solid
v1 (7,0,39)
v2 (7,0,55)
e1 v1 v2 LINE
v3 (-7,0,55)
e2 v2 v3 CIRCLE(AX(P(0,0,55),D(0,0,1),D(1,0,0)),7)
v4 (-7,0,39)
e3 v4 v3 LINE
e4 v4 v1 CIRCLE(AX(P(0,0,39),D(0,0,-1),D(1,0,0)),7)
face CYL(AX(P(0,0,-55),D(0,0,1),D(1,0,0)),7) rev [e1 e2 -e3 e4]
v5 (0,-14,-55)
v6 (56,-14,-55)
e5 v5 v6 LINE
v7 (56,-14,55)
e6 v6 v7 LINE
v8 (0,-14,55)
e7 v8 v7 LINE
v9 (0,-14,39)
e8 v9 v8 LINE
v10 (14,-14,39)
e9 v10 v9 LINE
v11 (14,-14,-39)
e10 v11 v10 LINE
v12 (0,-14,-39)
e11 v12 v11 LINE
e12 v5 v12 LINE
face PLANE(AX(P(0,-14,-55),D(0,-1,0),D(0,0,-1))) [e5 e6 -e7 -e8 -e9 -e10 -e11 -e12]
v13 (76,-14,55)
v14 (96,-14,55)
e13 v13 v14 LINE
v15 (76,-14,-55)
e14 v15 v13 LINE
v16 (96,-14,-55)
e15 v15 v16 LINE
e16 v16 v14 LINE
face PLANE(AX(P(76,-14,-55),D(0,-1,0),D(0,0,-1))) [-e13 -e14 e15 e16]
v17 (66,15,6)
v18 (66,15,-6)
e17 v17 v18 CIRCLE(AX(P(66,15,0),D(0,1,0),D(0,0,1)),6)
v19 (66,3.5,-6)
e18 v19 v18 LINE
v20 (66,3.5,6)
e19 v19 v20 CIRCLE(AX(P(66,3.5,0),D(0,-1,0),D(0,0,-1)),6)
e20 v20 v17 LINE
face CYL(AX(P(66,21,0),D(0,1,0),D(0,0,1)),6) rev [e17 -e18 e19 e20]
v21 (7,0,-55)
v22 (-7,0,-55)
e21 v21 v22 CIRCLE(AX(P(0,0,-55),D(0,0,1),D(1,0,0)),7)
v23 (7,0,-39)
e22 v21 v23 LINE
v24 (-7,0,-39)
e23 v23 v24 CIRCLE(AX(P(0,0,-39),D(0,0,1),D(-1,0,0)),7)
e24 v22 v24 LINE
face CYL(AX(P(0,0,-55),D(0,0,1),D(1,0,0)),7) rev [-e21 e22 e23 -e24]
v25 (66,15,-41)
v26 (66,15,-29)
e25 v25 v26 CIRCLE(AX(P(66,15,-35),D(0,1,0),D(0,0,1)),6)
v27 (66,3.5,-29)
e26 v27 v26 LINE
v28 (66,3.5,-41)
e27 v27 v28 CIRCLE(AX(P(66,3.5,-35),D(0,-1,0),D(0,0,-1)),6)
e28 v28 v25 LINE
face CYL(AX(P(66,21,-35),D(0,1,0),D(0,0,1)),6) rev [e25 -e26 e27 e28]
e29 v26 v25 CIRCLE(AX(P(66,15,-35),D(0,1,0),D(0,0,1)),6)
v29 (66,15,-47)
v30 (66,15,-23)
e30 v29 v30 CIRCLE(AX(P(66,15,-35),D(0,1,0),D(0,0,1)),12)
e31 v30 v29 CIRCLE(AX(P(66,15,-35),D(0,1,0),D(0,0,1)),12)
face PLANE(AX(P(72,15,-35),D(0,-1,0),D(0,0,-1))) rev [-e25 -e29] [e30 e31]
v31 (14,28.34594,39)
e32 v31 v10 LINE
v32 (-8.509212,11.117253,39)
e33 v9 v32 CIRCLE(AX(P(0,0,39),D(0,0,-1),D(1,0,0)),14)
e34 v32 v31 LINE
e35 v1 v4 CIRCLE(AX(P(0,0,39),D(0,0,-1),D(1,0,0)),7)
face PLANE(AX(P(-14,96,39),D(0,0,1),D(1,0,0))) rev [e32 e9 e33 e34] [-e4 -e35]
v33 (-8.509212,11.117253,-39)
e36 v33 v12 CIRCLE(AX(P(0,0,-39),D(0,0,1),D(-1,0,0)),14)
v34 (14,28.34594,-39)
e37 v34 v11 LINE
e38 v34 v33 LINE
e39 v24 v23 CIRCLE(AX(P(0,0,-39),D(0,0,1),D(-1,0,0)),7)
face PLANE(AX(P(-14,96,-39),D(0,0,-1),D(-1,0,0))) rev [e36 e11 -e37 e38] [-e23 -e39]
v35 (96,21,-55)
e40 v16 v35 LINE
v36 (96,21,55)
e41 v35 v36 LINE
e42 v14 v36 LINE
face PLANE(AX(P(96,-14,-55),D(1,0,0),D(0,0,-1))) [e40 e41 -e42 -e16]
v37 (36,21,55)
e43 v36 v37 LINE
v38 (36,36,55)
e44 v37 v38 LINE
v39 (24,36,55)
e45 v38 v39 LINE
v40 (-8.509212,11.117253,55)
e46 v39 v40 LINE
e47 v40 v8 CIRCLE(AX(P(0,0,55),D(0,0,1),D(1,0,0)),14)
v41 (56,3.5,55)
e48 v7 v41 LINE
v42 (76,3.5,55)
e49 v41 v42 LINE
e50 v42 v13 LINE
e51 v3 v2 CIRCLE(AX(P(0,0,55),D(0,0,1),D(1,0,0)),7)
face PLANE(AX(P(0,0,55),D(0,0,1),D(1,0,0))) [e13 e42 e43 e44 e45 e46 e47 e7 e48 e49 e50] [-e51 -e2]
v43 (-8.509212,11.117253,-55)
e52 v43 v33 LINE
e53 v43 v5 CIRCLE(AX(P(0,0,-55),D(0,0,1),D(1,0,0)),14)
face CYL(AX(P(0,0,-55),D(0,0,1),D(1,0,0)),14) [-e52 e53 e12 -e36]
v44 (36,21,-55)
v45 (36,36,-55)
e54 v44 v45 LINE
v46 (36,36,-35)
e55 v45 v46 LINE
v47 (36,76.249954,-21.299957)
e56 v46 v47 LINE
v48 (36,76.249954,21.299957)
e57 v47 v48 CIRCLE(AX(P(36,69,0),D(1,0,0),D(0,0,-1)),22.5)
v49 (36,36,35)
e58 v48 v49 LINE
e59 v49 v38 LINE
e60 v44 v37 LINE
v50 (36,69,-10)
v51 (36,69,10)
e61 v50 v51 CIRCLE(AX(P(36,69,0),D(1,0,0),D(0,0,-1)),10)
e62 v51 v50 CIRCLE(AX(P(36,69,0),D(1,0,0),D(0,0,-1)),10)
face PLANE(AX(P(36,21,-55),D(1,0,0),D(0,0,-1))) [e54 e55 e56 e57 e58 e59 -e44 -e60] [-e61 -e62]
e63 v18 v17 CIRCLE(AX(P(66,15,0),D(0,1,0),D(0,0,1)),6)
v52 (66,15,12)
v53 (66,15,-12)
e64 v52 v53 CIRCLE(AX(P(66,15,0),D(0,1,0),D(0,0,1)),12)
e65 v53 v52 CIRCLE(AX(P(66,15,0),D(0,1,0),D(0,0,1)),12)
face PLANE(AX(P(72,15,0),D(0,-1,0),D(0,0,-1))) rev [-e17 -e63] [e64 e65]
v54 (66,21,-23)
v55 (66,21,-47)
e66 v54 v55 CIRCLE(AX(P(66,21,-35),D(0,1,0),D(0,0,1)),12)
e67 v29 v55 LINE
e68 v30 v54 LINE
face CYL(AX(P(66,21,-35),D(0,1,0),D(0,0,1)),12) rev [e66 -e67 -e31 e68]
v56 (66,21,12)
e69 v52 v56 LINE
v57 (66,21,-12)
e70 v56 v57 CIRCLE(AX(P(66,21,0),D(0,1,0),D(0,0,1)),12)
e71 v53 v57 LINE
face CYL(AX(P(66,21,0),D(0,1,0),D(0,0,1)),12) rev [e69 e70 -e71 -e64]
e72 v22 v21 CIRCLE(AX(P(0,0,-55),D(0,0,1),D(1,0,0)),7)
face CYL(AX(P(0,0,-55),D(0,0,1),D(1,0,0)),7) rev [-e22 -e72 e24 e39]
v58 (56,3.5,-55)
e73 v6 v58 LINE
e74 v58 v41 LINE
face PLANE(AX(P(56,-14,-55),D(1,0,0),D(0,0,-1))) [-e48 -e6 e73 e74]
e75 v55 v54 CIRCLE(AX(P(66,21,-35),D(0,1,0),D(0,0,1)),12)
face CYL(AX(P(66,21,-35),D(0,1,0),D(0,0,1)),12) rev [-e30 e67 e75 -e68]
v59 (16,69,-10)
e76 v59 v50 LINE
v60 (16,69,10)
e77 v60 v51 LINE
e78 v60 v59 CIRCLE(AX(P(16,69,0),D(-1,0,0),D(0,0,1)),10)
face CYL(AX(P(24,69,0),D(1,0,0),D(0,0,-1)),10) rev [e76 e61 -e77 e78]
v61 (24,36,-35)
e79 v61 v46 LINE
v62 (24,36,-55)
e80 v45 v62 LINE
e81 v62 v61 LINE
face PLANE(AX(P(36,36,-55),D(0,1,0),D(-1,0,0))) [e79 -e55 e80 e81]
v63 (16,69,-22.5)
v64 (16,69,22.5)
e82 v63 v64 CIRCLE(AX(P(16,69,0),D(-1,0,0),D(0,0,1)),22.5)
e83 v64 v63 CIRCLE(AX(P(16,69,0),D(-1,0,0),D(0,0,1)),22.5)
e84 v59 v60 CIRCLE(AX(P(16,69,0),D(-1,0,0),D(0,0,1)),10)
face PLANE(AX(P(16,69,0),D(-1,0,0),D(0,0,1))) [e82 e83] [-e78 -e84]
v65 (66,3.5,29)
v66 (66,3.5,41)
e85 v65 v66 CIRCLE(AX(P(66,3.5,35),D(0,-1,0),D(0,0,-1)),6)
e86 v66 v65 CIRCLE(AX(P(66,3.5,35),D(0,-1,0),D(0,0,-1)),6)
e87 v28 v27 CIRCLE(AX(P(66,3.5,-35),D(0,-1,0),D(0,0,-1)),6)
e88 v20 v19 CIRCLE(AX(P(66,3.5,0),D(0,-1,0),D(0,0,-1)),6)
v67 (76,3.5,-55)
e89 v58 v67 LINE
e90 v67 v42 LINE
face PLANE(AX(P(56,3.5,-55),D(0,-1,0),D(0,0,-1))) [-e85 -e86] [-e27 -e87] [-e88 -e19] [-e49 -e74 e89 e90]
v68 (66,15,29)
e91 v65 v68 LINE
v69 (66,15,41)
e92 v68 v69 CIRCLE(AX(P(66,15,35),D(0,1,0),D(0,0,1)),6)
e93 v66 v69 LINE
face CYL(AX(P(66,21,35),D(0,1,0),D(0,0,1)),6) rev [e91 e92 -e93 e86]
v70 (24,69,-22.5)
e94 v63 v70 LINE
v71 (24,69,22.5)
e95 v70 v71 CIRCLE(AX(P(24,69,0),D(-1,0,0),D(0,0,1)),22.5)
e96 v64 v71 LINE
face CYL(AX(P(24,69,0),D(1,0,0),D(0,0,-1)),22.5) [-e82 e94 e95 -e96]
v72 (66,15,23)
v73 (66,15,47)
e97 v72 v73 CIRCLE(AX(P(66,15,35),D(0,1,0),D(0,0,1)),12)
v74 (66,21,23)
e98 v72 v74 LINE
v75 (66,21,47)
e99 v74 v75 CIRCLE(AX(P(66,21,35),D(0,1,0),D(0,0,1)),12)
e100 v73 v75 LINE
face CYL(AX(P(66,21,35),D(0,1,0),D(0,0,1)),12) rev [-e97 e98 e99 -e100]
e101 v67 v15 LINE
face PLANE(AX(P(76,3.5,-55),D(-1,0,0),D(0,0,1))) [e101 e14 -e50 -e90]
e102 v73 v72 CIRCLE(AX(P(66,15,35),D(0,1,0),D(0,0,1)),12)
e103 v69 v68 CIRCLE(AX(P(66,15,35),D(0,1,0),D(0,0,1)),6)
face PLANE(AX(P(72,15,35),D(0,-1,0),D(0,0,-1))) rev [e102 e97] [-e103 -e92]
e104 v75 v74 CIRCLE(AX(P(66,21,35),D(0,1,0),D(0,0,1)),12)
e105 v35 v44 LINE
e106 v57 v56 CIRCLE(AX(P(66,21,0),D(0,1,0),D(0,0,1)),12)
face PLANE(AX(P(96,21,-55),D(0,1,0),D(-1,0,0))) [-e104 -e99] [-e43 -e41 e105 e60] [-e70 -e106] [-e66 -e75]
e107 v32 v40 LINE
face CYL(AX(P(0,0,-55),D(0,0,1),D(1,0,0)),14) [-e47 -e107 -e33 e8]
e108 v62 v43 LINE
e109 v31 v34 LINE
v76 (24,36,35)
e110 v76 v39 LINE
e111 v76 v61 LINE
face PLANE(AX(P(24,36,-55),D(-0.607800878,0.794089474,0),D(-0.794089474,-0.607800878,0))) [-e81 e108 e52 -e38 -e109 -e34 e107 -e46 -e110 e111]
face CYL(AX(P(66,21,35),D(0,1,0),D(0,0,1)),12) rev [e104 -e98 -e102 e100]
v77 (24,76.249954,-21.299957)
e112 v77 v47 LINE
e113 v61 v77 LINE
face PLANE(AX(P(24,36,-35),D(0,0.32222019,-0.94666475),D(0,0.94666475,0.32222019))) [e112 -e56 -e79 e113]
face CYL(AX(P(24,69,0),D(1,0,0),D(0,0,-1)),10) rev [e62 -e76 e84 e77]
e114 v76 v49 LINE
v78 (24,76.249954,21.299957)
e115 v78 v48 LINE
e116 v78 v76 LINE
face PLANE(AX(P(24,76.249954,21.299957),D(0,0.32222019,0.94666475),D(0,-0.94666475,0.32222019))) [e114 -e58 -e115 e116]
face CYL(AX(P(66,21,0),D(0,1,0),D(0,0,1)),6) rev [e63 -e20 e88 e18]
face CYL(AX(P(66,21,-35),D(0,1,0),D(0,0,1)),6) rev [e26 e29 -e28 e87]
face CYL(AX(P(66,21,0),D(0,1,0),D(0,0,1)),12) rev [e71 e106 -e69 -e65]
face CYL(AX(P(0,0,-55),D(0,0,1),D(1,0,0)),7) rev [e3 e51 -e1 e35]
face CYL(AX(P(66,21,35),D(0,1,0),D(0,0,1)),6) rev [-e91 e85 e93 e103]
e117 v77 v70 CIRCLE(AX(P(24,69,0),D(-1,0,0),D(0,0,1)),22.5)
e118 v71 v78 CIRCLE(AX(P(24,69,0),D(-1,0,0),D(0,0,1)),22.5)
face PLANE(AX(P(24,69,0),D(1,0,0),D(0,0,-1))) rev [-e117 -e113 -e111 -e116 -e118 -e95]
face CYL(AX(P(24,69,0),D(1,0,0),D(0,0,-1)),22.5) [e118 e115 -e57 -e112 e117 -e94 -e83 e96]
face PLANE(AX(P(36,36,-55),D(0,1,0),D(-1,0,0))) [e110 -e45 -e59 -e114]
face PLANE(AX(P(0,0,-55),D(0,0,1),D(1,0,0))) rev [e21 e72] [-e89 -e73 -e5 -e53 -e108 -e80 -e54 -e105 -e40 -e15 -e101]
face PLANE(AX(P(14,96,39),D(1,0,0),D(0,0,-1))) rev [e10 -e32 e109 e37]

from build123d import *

# Parameters (mm, degrees)
BASE_PROFILE_SKETCH_R                = 7
BASE_BLOCK_DEPTH                     = 55
GUIDE_SLOT_SKETCH_W                  = 28
GUIDE_SLOT_SKETCH_H                  = 78
GUIDE_SLOT_16X16_DEPTH               = 110
PIVOT_LUG_SKETCH_R                   = 10
PIVOT_LUG_DEPTH                      = 12
LUG_SUPPORT_SKETCH_R                 = 22.5
LUG_SUPPORT_SKETCH_R_2               = 10
LUG_SUPPORT_BOSS_DEPTH               = 8
COUNTERBORED_HOLES_3X_12_D           = 12
COUNTERBORED_HOLES_3X_12_DEPTH       = 99.819837708
COUNTERBORED_HOLES_3X_12_CBORE_D     = 24
COUNTERBORED_HOLES_3X_12_CBORE_DEPTH = 6


with BuildPart() as part:
    # Base Profile Sketch → Base Block (new, symmetric)
    with BuildSketch(Plane.XY):
        with BuildLine():
            Line((0, -14), (56, -14))
            Line((56, -14), (56, 3.5))
            Line((56, 3.5), (76, 3.5))
            Line((76, 3.5), (76, -14))
            Line((76, -14), (96, -14))
            Line((96, -14), (96, 21))
            Line((96, 21), (36, 21))
            Line((36, 21), (36, 36))
            Line((36, 36), (24, 36))
            Line((24, 36), (-8.50921229, 11.117252638))
            ThreePointArc((-8.50921229, 11.117252638), (-13.259742398, -4.492129955), (0, -14))
        make_face()
        Circle(BASE_PROFILE_SKETCH_R, mode=Mode.SUBTRACT)
    extrude(amount=BASE_BLOCK_DEPTH, both=True)

    # Guide Slot Sketch → Guide Slot 16x16 (cut)
    with BuildSketch(Plane.XZ.offset(14)):
        Rectangle(GUIDE_SLOT_SKETCH_W, GUIDE_SLOT_SKETCH_H)
    extrude(amount=-GUIDE_SLOT_16X16_DEPTH, mode=Mode.SUBTRACT)

    # Pivot Lug Sketch → Pivot Lug (add)
    with BuildSketch(Plane(origin=(36, 0, 0), x_dir=(0, 0, -1), z_dir=(1, 0, 0))):
        with BuildLine():
            Line((35, 36), (21.299956881, 76.249954267))
            ThreePointArc((21.299956881, 76.249954267), (0, 91.5), (-21.299956881, 76.249954267))
            Line((-21.299956881, 76.249954267), (-35, 36))
            Line((-35, 36), (35, 36))
        make_face()
        with Locations((0, 69)):
            Circle(PIVOT_LUG_SKETCH_R, mode=Mode.SUBTRACT)
    extrude(amount=-PIVOT_LUG_DEPTH)

    # Lug Support Sketch → Lug Support Boss (add)
    with BuildSketch(Plane.ZY.offset(-24)):
        with Locations(Location((0, 69, 0), (0, 0, 161.202754194))):
            Circle(LUG_SUPPORT_SKETCH_R)
        with Locations(Location((0, 69, 0), (0, 0, 180))):
            Circle(LUG_SUPPORT_SKETCH_R_2, mode=Mode.SUBTRACT)
    extrude(amount=LUG_SUPPORT_BOSS_DEPTH)

    # Counterbored Holes 3xØ12
    with Locations(Plane(origin=(66, 21, 35), x_dir=(1, 0, 0), z_dir=(0, 1, 0))):
        with Locations((0, 0), (0, 35), (0, 70)):
            CounterBoreHole(COUNTERBORED_HOLES_3X_12_D / 2, COUNTERBORED_HOLES_3X_12_CBORE_D / 2, COUNTERBORED_HOLES_3X_12_CBORE_DEPTH, depth=COUNTERBORED_HOLES_3X_12_DEPTH)


solid = part.part
